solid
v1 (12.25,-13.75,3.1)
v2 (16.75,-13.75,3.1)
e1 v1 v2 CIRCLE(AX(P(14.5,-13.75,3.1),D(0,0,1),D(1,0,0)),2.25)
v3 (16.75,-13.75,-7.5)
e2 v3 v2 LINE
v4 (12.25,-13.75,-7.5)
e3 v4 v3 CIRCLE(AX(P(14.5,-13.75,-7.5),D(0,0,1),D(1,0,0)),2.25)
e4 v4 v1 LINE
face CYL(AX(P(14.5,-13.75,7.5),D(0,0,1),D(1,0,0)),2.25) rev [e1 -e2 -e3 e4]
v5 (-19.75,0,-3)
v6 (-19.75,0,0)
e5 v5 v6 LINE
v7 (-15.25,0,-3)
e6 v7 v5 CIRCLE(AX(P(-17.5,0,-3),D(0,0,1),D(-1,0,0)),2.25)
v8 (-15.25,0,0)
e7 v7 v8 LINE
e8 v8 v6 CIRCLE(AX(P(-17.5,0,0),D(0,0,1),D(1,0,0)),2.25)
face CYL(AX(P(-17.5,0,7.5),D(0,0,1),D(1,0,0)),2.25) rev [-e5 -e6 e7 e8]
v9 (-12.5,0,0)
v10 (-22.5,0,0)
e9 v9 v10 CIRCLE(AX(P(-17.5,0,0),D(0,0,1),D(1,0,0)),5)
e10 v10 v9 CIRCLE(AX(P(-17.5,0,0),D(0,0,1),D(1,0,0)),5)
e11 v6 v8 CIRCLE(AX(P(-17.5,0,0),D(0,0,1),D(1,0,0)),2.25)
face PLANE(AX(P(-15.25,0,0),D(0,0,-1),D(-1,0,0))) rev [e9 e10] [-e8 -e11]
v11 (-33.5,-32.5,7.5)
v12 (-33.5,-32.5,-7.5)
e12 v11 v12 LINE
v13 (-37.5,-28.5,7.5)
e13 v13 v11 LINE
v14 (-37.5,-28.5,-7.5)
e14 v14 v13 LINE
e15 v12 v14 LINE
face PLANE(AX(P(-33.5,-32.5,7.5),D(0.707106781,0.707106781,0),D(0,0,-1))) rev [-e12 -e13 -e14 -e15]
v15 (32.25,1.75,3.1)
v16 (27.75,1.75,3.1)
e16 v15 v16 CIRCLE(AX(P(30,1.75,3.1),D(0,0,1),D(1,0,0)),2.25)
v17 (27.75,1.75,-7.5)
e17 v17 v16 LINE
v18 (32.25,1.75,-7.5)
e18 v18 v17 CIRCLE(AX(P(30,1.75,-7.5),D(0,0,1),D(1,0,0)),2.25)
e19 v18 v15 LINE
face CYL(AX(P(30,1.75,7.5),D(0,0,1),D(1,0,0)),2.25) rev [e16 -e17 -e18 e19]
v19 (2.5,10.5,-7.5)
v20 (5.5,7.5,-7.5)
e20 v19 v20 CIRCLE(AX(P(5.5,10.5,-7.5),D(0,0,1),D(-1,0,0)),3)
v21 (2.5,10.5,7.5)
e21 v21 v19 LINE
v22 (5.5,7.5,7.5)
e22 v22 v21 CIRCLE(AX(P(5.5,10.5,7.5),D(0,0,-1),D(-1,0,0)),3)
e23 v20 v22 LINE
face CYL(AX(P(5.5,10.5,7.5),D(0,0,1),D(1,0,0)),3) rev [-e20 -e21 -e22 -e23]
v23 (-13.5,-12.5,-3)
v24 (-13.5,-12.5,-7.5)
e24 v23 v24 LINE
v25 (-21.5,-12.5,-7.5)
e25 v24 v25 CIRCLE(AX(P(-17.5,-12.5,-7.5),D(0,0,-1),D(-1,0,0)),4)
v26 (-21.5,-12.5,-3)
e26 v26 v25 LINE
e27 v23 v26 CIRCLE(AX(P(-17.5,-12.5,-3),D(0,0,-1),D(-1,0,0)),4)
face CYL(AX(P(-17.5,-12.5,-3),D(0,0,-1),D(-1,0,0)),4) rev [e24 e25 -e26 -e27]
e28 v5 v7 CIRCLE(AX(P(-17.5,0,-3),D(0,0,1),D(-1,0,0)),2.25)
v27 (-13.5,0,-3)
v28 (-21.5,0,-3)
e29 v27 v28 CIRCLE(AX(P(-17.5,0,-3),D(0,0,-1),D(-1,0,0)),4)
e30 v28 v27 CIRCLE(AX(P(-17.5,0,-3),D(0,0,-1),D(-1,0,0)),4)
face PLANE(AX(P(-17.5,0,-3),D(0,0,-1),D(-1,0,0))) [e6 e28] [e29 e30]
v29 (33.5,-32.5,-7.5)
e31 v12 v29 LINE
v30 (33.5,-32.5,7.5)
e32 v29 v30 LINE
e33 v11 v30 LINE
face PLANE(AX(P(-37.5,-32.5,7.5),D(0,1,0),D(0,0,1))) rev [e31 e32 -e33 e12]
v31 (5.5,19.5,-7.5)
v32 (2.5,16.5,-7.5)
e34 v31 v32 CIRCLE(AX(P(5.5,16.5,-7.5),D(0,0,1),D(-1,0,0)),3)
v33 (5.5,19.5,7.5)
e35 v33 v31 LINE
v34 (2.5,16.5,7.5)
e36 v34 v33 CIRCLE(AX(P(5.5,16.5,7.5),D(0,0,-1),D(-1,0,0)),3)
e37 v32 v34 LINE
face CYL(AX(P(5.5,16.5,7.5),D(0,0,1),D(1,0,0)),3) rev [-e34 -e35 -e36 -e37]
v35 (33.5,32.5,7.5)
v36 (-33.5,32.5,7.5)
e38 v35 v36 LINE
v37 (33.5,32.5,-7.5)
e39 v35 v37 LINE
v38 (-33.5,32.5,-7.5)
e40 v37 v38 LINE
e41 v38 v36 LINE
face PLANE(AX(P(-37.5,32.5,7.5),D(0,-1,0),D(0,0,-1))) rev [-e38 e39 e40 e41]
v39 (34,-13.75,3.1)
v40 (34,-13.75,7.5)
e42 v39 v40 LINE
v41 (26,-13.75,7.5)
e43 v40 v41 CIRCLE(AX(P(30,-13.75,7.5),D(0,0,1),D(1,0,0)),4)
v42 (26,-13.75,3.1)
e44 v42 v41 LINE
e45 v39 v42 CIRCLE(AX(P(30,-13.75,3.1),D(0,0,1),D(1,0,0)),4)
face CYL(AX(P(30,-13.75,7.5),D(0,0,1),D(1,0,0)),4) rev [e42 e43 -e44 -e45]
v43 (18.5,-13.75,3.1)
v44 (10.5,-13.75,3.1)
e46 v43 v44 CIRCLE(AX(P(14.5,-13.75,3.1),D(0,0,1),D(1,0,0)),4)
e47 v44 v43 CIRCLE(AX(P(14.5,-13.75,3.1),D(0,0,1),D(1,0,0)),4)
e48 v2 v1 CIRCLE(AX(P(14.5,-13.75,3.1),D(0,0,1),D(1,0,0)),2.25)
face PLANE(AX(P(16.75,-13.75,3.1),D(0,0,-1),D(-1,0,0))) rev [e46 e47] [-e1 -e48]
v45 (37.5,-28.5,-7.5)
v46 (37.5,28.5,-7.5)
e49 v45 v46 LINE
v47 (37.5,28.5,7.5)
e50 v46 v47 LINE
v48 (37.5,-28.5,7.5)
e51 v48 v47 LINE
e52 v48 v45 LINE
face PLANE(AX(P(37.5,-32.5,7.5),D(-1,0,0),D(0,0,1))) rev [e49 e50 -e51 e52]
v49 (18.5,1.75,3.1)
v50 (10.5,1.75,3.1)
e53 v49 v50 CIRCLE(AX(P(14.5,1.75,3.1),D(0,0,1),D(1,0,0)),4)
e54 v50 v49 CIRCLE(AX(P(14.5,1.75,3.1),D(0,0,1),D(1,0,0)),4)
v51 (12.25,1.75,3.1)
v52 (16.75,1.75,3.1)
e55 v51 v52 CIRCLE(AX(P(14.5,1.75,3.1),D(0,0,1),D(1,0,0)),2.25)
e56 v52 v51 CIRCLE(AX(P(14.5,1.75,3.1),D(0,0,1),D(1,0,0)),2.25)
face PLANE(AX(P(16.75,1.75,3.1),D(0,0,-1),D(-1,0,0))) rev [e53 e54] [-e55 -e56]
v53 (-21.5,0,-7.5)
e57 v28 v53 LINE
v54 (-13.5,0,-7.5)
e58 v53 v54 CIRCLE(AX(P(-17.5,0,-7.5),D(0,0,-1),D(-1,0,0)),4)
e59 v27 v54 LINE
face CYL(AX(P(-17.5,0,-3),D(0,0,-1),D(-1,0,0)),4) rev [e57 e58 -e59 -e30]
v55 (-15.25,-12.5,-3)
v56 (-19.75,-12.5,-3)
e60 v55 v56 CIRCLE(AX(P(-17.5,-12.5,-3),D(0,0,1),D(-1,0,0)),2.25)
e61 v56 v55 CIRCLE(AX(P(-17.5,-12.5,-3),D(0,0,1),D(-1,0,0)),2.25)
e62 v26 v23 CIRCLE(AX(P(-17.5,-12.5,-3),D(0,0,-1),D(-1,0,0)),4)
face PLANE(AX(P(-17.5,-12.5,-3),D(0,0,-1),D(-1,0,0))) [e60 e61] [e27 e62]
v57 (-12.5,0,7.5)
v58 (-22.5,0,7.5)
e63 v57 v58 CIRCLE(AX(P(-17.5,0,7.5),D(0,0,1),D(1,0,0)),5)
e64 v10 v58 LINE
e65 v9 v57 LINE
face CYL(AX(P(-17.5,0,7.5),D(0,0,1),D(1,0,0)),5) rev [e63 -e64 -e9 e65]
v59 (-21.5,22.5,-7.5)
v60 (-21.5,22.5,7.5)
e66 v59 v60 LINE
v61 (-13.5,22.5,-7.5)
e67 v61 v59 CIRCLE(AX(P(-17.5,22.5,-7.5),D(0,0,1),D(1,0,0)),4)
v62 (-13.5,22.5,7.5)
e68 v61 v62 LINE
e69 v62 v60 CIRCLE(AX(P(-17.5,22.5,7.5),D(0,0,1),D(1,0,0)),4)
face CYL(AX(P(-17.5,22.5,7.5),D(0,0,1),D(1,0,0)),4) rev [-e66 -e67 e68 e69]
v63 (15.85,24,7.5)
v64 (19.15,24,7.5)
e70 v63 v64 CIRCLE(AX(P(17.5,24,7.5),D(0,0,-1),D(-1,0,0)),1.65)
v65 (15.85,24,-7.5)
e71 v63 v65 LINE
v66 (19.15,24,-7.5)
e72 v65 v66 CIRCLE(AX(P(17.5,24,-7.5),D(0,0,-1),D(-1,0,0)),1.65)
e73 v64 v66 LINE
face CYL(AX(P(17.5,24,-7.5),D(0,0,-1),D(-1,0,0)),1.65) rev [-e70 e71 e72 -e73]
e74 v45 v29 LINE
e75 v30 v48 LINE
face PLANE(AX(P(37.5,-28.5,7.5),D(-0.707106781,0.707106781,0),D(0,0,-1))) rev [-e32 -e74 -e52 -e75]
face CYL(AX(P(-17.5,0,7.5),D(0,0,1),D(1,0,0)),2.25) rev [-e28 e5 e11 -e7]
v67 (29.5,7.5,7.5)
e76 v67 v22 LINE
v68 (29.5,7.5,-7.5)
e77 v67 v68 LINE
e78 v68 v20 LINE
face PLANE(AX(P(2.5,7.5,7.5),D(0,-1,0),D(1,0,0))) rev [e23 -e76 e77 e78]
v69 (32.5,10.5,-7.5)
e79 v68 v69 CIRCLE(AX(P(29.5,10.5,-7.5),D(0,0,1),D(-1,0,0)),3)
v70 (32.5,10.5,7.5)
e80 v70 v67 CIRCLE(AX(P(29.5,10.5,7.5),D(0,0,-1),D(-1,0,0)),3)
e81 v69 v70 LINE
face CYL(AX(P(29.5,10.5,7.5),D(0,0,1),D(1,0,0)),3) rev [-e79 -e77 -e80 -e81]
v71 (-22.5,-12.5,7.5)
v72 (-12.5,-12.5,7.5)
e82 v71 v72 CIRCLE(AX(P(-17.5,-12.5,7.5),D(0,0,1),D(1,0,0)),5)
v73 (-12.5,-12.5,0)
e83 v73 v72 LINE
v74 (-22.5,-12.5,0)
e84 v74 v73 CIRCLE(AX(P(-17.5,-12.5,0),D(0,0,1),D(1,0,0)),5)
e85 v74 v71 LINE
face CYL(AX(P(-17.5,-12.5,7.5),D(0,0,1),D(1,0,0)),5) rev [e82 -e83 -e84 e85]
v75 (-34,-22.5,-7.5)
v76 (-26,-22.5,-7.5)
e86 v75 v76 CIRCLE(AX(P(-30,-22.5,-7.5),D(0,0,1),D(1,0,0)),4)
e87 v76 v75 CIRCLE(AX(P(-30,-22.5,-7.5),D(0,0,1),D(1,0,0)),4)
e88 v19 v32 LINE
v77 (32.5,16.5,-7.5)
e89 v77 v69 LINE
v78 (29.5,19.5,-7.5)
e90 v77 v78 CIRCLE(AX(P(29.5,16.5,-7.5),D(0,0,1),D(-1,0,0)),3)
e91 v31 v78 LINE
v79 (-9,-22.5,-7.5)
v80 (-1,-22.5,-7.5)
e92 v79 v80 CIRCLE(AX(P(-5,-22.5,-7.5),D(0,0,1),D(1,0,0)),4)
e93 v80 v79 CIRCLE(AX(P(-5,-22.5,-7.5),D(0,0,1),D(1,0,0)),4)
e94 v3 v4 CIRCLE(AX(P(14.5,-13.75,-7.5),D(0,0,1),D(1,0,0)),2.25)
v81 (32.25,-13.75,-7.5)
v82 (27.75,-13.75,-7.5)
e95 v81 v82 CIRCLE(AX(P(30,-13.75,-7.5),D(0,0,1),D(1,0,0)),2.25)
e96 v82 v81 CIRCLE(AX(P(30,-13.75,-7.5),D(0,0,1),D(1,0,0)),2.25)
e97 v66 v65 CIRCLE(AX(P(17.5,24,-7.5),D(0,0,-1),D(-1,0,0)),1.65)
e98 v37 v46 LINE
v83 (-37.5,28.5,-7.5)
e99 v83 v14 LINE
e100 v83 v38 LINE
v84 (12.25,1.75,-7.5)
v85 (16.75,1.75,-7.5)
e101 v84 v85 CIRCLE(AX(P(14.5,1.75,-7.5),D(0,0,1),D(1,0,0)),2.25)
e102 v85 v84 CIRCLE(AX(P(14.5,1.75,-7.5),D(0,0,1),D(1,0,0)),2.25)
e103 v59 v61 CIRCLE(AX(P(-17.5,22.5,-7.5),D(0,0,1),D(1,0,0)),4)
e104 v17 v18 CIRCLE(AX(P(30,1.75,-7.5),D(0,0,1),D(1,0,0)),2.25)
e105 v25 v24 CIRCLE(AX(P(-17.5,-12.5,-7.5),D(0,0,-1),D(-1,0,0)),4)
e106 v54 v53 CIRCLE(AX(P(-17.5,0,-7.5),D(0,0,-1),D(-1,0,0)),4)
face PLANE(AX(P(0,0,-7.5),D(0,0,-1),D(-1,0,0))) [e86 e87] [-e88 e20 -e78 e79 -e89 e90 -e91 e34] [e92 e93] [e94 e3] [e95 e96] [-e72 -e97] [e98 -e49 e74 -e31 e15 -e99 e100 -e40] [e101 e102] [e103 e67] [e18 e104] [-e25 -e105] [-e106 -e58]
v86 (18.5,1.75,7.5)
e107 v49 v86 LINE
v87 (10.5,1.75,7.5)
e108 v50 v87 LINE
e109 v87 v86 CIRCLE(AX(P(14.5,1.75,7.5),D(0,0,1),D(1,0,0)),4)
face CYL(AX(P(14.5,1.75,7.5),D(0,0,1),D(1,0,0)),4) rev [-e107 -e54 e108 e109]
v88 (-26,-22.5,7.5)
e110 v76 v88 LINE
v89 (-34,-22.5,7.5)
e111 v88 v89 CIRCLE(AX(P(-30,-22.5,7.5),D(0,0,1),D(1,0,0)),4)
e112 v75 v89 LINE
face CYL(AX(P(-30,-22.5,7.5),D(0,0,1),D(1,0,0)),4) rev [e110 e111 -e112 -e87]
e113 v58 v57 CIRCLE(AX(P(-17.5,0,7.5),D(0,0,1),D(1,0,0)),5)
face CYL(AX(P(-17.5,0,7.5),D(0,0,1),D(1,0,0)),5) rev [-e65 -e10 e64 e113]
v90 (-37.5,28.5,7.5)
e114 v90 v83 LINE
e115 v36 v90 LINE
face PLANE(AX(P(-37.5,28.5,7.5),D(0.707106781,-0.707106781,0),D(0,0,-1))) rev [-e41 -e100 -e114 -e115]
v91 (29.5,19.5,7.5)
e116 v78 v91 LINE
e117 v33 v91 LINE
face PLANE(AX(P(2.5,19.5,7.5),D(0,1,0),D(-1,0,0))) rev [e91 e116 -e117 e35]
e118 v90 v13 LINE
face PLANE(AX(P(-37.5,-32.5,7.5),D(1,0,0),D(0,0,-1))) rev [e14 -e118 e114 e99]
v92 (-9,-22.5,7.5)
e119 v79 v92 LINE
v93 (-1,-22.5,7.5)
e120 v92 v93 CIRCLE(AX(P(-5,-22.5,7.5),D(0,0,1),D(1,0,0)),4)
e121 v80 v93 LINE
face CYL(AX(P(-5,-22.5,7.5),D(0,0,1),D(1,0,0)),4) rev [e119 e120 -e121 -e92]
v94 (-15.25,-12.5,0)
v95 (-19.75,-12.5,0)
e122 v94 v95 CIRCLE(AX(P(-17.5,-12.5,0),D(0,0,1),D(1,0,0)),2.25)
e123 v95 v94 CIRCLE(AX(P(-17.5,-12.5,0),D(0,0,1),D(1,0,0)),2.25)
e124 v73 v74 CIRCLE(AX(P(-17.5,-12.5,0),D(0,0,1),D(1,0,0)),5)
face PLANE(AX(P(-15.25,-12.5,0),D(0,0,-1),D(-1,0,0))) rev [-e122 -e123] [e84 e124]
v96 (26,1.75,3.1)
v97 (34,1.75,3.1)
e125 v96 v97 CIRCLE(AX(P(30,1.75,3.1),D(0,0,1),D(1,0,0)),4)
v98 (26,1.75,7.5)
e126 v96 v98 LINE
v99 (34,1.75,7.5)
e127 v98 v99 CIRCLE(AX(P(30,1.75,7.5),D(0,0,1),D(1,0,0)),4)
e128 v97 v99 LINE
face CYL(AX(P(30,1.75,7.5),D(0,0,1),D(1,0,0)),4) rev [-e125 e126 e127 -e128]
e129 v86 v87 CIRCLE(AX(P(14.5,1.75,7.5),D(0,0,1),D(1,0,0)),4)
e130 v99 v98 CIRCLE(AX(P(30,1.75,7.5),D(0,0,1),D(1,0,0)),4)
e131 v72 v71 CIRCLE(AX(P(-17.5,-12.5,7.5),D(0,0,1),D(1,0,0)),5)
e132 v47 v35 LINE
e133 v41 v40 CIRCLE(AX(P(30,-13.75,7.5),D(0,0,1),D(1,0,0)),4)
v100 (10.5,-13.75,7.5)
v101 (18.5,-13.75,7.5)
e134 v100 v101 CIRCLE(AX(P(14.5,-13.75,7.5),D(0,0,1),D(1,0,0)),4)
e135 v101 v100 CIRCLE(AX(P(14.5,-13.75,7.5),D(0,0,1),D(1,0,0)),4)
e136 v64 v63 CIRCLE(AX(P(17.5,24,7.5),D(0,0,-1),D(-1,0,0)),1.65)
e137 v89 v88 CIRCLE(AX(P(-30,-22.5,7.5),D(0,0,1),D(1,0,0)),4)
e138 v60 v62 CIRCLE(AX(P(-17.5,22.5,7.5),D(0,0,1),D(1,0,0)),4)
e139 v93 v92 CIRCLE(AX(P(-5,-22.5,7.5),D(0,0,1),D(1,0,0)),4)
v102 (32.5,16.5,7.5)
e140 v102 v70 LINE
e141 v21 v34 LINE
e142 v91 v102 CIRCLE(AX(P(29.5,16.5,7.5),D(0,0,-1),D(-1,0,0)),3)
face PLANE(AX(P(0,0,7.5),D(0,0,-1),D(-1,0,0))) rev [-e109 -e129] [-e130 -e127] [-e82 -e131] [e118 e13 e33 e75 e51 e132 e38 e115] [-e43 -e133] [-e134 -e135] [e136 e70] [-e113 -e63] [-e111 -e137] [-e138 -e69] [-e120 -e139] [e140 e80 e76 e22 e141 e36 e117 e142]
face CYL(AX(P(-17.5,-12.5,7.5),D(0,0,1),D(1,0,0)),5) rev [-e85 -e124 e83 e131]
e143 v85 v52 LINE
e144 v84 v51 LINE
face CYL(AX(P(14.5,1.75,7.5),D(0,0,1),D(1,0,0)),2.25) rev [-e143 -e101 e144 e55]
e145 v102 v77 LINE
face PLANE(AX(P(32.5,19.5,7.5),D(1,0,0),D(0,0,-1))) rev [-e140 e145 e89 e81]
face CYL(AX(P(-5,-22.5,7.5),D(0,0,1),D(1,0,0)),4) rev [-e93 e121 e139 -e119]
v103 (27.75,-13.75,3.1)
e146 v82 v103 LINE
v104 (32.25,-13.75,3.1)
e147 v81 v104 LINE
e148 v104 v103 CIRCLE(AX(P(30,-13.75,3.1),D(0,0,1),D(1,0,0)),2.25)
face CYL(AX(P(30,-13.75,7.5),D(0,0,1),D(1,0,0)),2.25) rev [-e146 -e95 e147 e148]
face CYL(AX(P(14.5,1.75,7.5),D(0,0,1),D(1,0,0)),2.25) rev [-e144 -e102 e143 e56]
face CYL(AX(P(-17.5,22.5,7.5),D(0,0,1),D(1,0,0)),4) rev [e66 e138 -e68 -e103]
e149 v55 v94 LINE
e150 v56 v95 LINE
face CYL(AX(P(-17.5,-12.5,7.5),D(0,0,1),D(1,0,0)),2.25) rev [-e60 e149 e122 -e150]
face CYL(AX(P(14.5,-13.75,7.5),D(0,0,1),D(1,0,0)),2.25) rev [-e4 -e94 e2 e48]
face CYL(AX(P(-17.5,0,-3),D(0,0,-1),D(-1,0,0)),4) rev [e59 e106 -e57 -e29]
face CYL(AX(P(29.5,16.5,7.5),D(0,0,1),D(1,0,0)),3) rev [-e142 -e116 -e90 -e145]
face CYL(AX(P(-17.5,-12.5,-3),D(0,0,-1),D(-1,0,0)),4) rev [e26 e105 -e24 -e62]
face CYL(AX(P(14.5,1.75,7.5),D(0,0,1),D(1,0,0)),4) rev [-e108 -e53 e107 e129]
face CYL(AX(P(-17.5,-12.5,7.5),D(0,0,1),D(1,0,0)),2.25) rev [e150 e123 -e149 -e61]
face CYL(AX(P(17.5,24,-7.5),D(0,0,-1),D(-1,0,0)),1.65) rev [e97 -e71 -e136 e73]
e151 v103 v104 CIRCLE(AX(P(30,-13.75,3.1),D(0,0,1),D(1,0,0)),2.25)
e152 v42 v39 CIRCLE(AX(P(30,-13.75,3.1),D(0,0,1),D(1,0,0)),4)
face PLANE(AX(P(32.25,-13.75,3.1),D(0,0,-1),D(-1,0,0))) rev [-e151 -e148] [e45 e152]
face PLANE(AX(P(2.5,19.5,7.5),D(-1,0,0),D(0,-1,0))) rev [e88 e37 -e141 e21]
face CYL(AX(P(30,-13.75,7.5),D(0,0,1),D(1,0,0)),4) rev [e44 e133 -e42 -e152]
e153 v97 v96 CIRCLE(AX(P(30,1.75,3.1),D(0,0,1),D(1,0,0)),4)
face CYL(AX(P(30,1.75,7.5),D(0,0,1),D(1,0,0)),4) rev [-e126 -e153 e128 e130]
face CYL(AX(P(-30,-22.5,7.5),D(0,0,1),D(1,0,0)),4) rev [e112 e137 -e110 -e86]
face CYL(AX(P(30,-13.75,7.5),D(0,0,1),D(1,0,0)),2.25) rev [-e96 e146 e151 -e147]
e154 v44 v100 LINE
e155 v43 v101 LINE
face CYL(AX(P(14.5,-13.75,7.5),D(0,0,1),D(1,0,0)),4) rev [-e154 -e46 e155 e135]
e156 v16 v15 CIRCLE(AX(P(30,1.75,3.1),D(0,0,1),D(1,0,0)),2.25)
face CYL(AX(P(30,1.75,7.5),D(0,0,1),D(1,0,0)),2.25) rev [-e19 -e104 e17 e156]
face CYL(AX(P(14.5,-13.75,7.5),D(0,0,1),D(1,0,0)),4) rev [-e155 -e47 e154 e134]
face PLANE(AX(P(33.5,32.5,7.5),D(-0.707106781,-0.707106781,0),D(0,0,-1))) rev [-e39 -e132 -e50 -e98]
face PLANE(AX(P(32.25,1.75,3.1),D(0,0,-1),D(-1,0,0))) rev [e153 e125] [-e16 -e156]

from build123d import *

# Parameters (mm, degrees)
SKETCH_1_W                   = 75
SKETCH_1_H                   = 65
EXTRUDE_1_DEPTH              = 7.5
HOLE_WIZARD_M4_1_D           = 4.5
HOLE_WIZARD_M4_1_CBORE_D     = 8
HOLE_WIZARD_M4_1_CBORE_DEPTH = 4.4
HOLE_WIZARD_8_0_8_1_D        = 8
HOLE_WIZARD_1_D              = 4.5
HOLE_WIZARD_1_CBORE_D        = 10
HOLE_WIZARD_1_CBORE_DEPTH    = 7.5
SKETCH_8_R                   = 4
CUT_EXTRUDE_1_DEPTH          = 4.5
CHAMFER_1_SIZE               = 4
SKETCH_9_W                   = 30
SKETCH_9_H                   = 12
CUT_EXTRUDE_2_DEPTH          = 52.841103383
HOLE_WIZARD_M4_1_2_D         = 3.3
FILLET_1_R                   = 3


with BuildPart() as part:
    # 草图1 → 凸台-拉伸1 (new, symmetric)
    with BuildSketch(Plane.XY):
        Rectangle(SKETCH_1_W, SKETCH_1_H)
    extrude(amount=EXTRUDE_1_DEPTH, both=True)

    # Hole Wizard M4 _1 (through all)
    with Locations(Plane.XY.offset(7.5)):
        with Locations((14.5, 1.75), (14.5, -13.75), (30, 1.75), (30, -13.75)):
            CounterBoreHole(HOLE_WIZARD_M4_1_D / 2, HOLE_WIZARD_M4_1_CBORE_D / 2, HOLE_WIZARD_M4_1_CBORE_DEPTH)

    # Ø8.0 (8) 直径孔1 (through all)
    with Locations(Plane.XY.offset(7.5)):
        with Locations((-17.5, 22.5), (-30, -22.5), (-5, -22.5)):
            Hole(HOLE_WIZARD_8_0_8_1_D / 2)

    # 孔1 (through all)
    with Locations(Plane.XY.offset(7.5)):
        with Locations((-17.5, 0), (-17.5, -12.5)):
            CounterBoreHole(HOLE_WIZARD_1_D / 2, HOLE_WIZARD_1_CBORE_D / 2, HOLE_WIZARD_1_CBORE_DEPTH)

    # 草图8 → 切除-拉伸1 (cut)
    with BuildSketch(Plane(origin=(0, 0, -7.5), x_dir=(-1, 0, 0), z_dir=(0, 0, -1))):
        with Locations((17.5, 0)):
            Circle(SKETCH_8_R)
        with Locations((17.5, -12.5)):
            Circle(SKETCH_8_R)
    extrude(amount=-CUT_EXTRUDE_1_DEPTH, mode=Mode.SUBTRACT)

    # 倒角1
    chamfer_1_edges = [part.edges().sort_by_distance(p)[0] for p in [
        (37.5, -32.5, 0),
        (-37.5, -32.5, 0),
        (-37.5, 32.5, 0),
        (37.5, 32.5, 0),
    ]]
    chamfer(chamfer_1_edges, length=CHAMFER_1_SIZE)

    # 草图9 → 切除-拉伸2 (cut, through all)
    with BuildSketch(Plane(origin=(0, 0, -7.5), x_dir=(-1, 0, 0), z_dir=(0, 0, -1))):
        with Locations((-17.5, 13.5)):
            Rectangle(SKETCH_9_W, SKETCH_9_H)
    extrude(amount=-CUT_EXTRUDE_2_DEPTH, mode=Mode.SUBTRACT)

    # Hole Wizard M4 _1 2 (through all)
    with Locations(Plane(origin=(0, 0, -7.5), x_dir=(-1, 0, 0), z_dir=(0, 0, -1))):
        with Locations((-17.5, 24)):
            Hole(HOLE_WIZARD_M4_1_2_D / 2)

    # 圆角1
    fillet_1_edges = [part.edges().sort_by_distance(p)[0] for p in [
        (2.5, 19.5, 0),
        (2.5, 7.5, 0),
        (32.5, 7.5, 0),
        (32.5, 19.5, 0),
    ]]
    fillet(fillet_1_edges, radius=FILLET_1_R)


solid = part.part
